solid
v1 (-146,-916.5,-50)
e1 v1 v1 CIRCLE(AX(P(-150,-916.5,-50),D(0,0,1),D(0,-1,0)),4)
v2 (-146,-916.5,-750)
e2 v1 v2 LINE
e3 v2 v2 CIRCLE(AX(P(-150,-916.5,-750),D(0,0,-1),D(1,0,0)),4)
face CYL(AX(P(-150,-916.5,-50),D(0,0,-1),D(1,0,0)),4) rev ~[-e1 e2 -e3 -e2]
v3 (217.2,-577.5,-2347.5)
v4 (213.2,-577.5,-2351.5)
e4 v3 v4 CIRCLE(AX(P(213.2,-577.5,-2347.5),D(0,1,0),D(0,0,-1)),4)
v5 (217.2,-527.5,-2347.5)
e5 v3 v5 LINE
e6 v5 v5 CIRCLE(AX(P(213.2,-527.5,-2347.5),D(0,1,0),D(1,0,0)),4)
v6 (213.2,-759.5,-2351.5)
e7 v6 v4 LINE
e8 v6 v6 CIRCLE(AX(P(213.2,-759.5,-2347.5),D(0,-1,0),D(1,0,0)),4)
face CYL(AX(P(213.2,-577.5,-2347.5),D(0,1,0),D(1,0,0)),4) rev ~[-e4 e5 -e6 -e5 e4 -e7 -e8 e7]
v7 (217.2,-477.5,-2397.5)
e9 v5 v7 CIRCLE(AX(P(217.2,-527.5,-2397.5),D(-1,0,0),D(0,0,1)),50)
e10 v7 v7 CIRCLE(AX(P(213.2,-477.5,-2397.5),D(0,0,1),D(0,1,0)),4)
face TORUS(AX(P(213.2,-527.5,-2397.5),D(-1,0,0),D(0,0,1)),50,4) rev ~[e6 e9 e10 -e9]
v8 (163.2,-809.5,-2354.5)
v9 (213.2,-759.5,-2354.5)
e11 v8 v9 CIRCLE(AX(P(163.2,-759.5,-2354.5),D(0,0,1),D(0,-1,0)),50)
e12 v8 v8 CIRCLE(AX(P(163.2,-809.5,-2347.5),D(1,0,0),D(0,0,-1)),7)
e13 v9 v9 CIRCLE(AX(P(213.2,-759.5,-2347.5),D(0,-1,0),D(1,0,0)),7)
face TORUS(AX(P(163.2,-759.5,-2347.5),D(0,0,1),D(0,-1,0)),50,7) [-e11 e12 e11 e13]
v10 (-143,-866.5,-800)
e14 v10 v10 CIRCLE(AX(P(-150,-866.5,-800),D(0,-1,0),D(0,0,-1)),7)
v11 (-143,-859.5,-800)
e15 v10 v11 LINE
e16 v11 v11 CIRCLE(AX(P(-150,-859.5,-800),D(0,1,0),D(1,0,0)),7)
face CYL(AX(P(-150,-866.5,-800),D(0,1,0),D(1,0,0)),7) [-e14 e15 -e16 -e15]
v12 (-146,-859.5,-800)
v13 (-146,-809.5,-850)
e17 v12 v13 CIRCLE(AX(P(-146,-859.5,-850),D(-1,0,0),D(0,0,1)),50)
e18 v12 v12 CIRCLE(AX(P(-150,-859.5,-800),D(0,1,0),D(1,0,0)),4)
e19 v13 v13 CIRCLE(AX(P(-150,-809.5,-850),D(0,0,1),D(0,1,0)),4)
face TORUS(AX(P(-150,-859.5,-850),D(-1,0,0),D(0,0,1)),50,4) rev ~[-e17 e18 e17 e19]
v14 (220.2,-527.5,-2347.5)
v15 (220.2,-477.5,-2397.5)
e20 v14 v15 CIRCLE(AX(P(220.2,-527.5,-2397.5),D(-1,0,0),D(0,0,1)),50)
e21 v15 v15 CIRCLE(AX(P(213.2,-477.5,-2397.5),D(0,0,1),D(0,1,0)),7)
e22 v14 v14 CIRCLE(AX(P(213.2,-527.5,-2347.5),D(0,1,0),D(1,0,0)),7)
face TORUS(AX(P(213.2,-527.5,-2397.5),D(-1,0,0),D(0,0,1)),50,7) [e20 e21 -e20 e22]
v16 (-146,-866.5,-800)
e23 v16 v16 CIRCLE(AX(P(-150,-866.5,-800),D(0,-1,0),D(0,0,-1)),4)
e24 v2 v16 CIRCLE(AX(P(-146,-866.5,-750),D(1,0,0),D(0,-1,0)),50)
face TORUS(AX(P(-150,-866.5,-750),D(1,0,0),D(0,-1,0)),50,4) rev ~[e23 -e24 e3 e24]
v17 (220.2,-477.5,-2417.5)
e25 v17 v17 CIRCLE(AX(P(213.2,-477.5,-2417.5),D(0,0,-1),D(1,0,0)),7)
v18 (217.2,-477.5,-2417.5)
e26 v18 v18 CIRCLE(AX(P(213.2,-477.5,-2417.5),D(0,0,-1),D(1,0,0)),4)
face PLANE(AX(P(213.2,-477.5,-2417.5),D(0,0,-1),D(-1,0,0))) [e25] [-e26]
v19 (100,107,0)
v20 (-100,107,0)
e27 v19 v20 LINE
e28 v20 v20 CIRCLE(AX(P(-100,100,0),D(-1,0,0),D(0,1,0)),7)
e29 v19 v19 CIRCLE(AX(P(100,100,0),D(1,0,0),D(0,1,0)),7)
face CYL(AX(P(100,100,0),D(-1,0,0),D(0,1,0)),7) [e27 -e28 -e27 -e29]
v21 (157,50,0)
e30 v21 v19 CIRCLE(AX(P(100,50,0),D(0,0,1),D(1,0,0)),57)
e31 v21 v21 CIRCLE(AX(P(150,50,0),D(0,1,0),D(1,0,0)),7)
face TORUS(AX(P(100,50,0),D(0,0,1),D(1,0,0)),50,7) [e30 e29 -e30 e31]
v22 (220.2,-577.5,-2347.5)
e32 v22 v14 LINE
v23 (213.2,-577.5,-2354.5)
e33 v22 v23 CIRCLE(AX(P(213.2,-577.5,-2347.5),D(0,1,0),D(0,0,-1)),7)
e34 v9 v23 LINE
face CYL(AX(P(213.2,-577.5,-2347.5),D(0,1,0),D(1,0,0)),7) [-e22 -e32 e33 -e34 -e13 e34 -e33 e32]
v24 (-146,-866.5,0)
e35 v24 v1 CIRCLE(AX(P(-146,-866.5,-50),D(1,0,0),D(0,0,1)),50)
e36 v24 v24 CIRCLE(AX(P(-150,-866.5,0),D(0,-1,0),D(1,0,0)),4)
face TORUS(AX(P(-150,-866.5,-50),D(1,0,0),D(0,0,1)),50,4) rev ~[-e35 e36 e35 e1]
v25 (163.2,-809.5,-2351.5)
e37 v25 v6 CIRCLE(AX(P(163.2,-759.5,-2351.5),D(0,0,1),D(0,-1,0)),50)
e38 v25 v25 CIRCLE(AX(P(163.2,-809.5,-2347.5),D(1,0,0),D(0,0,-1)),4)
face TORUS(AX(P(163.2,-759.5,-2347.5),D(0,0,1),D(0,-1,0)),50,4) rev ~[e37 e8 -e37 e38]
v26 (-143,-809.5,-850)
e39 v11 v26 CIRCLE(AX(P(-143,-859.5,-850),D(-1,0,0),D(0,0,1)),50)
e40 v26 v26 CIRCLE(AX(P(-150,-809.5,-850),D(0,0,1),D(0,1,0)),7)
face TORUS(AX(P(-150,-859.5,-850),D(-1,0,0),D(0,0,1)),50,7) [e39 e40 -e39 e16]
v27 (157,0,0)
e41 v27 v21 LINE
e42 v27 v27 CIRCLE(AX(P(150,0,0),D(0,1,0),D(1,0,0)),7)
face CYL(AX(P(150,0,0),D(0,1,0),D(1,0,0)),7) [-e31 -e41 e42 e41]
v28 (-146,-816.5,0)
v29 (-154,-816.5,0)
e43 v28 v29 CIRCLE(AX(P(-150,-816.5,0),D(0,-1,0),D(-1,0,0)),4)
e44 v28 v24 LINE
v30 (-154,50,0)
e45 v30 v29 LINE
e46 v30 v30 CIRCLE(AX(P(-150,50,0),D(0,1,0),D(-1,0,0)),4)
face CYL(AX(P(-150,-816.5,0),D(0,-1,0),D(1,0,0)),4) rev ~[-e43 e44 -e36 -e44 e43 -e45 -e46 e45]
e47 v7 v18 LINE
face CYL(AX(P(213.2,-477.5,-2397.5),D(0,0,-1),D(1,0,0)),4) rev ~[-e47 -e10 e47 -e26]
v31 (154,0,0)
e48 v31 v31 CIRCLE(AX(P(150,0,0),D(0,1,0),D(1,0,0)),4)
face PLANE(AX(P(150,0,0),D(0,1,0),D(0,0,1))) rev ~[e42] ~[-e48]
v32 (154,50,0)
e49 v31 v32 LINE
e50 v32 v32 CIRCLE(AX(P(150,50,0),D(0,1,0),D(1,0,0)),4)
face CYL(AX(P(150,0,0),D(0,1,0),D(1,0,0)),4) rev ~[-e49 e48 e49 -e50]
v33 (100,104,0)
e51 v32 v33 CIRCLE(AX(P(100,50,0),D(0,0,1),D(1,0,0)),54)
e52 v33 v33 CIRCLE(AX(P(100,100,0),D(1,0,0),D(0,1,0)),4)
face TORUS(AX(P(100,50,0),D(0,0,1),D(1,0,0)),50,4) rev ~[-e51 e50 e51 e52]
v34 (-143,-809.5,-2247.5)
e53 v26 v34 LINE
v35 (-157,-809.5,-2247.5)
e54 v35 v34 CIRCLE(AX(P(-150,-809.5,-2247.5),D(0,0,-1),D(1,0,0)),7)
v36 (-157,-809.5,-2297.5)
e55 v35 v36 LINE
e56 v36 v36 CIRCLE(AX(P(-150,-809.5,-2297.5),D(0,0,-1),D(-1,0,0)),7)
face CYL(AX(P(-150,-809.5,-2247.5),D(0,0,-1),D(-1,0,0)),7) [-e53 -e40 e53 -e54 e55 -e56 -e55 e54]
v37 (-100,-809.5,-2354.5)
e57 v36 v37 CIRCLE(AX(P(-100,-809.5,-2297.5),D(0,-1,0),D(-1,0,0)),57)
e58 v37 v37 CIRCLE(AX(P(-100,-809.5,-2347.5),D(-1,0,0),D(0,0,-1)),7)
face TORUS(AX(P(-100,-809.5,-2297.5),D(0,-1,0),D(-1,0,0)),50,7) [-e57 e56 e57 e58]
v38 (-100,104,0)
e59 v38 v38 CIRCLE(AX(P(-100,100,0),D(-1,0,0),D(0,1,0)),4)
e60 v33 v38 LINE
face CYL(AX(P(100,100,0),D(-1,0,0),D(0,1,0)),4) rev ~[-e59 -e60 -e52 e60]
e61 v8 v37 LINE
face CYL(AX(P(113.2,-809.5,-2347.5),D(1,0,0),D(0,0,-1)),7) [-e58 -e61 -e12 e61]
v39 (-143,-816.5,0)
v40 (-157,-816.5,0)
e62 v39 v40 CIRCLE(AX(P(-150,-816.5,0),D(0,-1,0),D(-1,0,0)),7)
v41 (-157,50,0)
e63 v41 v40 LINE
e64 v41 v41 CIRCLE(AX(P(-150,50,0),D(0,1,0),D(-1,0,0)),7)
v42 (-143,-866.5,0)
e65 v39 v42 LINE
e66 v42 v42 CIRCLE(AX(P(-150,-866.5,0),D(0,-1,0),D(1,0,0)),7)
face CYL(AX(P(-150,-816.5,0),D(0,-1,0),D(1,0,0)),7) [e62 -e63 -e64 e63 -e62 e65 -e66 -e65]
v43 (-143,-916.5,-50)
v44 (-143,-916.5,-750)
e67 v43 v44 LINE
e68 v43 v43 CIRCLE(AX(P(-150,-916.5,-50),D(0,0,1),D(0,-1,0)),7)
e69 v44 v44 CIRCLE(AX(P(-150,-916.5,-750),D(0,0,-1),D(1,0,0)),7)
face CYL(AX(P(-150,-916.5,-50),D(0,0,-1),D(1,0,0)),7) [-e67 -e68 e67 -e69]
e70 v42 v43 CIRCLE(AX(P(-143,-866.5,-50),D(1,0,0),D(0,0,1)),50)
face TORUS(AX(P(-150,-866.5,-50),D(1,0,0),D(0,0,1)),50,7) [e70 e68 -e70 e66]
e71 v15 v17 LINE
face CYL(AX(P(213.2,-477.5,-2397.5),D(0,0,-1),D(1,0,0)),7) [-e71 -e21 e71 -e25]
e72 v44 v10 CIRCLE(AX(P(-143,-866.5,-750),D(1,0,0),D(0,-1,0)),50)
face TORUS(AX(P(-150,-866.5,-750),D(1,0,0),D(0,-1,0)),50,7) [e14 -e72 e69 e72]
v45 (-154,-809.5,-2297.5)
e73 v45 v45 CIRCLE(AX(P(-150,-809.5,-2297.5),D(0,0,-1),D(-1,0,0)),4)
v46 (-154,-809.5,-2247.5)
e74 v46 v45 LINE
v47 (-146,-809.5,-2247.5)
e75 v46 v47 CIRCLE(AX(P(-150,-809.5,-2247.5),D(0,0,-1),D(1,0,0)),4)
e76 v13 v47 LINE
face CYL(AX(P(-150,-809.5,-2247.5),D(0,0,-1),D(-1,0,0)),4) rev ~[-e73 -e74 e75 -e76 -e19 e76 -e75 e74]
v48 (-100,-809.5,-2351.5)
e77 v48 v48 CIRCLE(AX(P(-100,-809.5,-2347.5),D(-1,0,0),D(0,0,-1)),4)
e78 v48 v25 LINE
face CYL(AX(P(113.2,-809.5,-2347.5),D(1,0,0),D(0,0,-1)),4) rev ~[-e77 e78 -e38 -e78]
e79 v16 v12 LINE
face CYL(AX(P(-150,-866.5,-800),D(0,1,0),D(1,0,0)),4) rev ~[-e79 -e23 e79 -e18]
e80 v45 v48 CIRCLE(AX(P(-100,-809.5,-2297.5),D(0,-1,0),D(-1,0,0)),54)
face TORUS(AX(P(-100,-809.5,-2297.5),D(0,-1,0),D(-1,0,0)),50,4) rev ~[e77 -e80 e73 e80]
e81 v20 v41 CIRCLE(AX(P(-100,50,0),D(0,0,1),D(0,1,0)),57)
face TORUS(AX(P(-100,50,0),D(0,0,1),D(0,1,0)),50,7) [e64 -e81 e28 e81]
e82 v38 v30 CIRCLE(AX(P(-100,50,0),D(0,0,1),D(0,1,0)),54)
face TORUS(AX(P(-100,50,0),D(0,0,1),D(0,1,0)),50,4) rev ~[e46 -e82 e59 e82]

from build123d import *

# Parameters (mm, degrees)
SKETCH_2_R    = 7
SKETCH_2_R_2  = 4
SKETCH_4_R    = 7
SKETCH_4_R_2  = 4
SKETCH_6_R    = 7
SKETCH_6_R_2  = 4
SKETCH_8_R    = 7
SKETCH_8_R_2  = 4
SKETCH_10_R   = 7
SKETCH_10_R_2 = 4


with BuildPart() as part:
    # Sweep 1: sweep along a path in Sketch 1
    with BuildLine(Plane.XY) as sweep_1_path:
        Line((150, 0), (150, 50))
        ThreePointArc((150, 50), (135.355339059, 85.355339059), (100, 100))
        Line((100, 100), (-100, 100))
        ThreePointArc((-100, 100), (-135.355339059, 85.355339059), (-150, 50))
        Line((-150, 50), (-150, -816.5))
    # Sketch 2 → Sweep 1 (sweep)
    with BuildSketch(Plane(origin=(0, 0, 0), x_dir=(1, 0, 0), z_dir=(0, 1, 0))):
        with Locations((150, 0)):
            Circle(SKETCH_2_R)
        with Locations((150, 0)):
            Circle(SKETCH_2_R_2, mode=Mode.SUBTRACT)
    sweep(path=sweep_1_path.line)

    # Sweep 2: sweep along a path in Sketch 3
    with BuildLine(Plane(origin=(-150, 0, 0), x_dir=(0, 0, -1), z_dir=(1, 0, 0))) as sweep_2_path:
        Line((0, -816.5), (0, -866.5))
        ThreePointArc((0, -866.5), (14.644660941, -901.855339059), (50, -916.5))
        Line((50, -916.5), (750, -916.5))
        ThreePointArc((750, -916.5), (785.355339059, -901.855339059), (800, -866.5))
        Line((800, -866.5), (800, -859.5))
        ThreePointArc((800, -859.5), (814.644660941, -824.144660941), (850, -809.5))
        Line((850, -809.5), (2247.5, -809.5))
    # Sketch 4 → Sweep 2 (sweep)
    with BuildSketch(Plane.XZ.offset(816.5)):
        with Locations((-150, 0)):
            Circle(SKETCH_4_R)
        with Locations((-150, 0)):
            Circle(SKETCH_4_R_2, mode=Mode.SUBTRACT)
    sweep(path=sweep_2_path.line)

    # Sweep 3: sweep along a path in Sketch 5
    with BuildLine(Plane(origin=(0, -809.5, 0), x_dir=(1, 0, 0), z_dir=(0, 1, 0))) as sweep_3_path:
        Line((-150, 2247.5), (-150, 2297.5))
        ThreePointArc((-150, 2297.5), (-135.355339059, 2332.855339059), (-100, 2347.5))
        Line((-100, 2347.5), (113.2, 2347.5))
    # Sketch 6 → Sweep 3 (sweep)
    with BuildSketch(Plane(origin=(0, 0, -2247.5), x_dir=(-1, 0, 0), z_dir=(0, 0, -1))):
        with Locations((150, -809.5)):
            Circle(SKETCH_6_R)
        with Locations((150, -809.5)):
            Circle(SKETCH_6_R_2, mode=Mode.SUBTRACT)
    sweep(path=sweep_3_path.line)

    # Sweep 4: sweep along a path in Sketch 7
    with BuildLine(Plane.XY.offset(-2347.5)) as sweep_4_path:
        Line((113.2, -809.5), (163.2, -809.5))
        ThreePointArc((163.2, -809.5), (198.555339059, -794.855339059), (213.2, -759.5))
        Line((213.2, -759.5), (213.2, -577.5))
    # Sketch 8 → Sweep 4 (sweep)
    with BuildSketch(Plane(origin=(113.2, 0, 0), x_dir=(0, 0, -1), z_dir=(1, 0, 0))):
        with Locations((2347.5, -809.5)):
            Circle(SKETCH_8_R)
        with Locations((2347.5, -809.5)):
            Circle(SKETCH_8_R_2, mode=Mode.SUBTRACT)
    sweep(path=sweep_4_path.line)

    # Sweep 5: sweep along a path in Sketch 9
    with BuildLine(Plane(origin=(213.2, 0, 0), x_dir=(0, 0, -1), z_dir=(1, 0, 0))) as sweep_5_path:
        Line((2347.5, -577.5), (2347.5, -527.5))
        ThreePointArc((2347.5, -527.5), (2362.144660941, -492.144660941), (2397.5, -477.5))
        Line((2397.5, -477.5), (2417.5, -477.5))
    # Sketch 10 → Sweep 5 (sweep)
    with BuildSketch(Plane(origin=(0, -577.5, 0), x_dir=(1, 0, 0), z_dir=(0, 1, 0))):
        with Locations((213.2, 2347.5)):
            Circle(SKETCH_10_R)
        with Locations((213.2, 2347.5)):
            Circle(SKETCH_10_R_2, mode=Mode.SUBTRACT)
    sweep(path=sweep_5_path.line)


solid = part.part
